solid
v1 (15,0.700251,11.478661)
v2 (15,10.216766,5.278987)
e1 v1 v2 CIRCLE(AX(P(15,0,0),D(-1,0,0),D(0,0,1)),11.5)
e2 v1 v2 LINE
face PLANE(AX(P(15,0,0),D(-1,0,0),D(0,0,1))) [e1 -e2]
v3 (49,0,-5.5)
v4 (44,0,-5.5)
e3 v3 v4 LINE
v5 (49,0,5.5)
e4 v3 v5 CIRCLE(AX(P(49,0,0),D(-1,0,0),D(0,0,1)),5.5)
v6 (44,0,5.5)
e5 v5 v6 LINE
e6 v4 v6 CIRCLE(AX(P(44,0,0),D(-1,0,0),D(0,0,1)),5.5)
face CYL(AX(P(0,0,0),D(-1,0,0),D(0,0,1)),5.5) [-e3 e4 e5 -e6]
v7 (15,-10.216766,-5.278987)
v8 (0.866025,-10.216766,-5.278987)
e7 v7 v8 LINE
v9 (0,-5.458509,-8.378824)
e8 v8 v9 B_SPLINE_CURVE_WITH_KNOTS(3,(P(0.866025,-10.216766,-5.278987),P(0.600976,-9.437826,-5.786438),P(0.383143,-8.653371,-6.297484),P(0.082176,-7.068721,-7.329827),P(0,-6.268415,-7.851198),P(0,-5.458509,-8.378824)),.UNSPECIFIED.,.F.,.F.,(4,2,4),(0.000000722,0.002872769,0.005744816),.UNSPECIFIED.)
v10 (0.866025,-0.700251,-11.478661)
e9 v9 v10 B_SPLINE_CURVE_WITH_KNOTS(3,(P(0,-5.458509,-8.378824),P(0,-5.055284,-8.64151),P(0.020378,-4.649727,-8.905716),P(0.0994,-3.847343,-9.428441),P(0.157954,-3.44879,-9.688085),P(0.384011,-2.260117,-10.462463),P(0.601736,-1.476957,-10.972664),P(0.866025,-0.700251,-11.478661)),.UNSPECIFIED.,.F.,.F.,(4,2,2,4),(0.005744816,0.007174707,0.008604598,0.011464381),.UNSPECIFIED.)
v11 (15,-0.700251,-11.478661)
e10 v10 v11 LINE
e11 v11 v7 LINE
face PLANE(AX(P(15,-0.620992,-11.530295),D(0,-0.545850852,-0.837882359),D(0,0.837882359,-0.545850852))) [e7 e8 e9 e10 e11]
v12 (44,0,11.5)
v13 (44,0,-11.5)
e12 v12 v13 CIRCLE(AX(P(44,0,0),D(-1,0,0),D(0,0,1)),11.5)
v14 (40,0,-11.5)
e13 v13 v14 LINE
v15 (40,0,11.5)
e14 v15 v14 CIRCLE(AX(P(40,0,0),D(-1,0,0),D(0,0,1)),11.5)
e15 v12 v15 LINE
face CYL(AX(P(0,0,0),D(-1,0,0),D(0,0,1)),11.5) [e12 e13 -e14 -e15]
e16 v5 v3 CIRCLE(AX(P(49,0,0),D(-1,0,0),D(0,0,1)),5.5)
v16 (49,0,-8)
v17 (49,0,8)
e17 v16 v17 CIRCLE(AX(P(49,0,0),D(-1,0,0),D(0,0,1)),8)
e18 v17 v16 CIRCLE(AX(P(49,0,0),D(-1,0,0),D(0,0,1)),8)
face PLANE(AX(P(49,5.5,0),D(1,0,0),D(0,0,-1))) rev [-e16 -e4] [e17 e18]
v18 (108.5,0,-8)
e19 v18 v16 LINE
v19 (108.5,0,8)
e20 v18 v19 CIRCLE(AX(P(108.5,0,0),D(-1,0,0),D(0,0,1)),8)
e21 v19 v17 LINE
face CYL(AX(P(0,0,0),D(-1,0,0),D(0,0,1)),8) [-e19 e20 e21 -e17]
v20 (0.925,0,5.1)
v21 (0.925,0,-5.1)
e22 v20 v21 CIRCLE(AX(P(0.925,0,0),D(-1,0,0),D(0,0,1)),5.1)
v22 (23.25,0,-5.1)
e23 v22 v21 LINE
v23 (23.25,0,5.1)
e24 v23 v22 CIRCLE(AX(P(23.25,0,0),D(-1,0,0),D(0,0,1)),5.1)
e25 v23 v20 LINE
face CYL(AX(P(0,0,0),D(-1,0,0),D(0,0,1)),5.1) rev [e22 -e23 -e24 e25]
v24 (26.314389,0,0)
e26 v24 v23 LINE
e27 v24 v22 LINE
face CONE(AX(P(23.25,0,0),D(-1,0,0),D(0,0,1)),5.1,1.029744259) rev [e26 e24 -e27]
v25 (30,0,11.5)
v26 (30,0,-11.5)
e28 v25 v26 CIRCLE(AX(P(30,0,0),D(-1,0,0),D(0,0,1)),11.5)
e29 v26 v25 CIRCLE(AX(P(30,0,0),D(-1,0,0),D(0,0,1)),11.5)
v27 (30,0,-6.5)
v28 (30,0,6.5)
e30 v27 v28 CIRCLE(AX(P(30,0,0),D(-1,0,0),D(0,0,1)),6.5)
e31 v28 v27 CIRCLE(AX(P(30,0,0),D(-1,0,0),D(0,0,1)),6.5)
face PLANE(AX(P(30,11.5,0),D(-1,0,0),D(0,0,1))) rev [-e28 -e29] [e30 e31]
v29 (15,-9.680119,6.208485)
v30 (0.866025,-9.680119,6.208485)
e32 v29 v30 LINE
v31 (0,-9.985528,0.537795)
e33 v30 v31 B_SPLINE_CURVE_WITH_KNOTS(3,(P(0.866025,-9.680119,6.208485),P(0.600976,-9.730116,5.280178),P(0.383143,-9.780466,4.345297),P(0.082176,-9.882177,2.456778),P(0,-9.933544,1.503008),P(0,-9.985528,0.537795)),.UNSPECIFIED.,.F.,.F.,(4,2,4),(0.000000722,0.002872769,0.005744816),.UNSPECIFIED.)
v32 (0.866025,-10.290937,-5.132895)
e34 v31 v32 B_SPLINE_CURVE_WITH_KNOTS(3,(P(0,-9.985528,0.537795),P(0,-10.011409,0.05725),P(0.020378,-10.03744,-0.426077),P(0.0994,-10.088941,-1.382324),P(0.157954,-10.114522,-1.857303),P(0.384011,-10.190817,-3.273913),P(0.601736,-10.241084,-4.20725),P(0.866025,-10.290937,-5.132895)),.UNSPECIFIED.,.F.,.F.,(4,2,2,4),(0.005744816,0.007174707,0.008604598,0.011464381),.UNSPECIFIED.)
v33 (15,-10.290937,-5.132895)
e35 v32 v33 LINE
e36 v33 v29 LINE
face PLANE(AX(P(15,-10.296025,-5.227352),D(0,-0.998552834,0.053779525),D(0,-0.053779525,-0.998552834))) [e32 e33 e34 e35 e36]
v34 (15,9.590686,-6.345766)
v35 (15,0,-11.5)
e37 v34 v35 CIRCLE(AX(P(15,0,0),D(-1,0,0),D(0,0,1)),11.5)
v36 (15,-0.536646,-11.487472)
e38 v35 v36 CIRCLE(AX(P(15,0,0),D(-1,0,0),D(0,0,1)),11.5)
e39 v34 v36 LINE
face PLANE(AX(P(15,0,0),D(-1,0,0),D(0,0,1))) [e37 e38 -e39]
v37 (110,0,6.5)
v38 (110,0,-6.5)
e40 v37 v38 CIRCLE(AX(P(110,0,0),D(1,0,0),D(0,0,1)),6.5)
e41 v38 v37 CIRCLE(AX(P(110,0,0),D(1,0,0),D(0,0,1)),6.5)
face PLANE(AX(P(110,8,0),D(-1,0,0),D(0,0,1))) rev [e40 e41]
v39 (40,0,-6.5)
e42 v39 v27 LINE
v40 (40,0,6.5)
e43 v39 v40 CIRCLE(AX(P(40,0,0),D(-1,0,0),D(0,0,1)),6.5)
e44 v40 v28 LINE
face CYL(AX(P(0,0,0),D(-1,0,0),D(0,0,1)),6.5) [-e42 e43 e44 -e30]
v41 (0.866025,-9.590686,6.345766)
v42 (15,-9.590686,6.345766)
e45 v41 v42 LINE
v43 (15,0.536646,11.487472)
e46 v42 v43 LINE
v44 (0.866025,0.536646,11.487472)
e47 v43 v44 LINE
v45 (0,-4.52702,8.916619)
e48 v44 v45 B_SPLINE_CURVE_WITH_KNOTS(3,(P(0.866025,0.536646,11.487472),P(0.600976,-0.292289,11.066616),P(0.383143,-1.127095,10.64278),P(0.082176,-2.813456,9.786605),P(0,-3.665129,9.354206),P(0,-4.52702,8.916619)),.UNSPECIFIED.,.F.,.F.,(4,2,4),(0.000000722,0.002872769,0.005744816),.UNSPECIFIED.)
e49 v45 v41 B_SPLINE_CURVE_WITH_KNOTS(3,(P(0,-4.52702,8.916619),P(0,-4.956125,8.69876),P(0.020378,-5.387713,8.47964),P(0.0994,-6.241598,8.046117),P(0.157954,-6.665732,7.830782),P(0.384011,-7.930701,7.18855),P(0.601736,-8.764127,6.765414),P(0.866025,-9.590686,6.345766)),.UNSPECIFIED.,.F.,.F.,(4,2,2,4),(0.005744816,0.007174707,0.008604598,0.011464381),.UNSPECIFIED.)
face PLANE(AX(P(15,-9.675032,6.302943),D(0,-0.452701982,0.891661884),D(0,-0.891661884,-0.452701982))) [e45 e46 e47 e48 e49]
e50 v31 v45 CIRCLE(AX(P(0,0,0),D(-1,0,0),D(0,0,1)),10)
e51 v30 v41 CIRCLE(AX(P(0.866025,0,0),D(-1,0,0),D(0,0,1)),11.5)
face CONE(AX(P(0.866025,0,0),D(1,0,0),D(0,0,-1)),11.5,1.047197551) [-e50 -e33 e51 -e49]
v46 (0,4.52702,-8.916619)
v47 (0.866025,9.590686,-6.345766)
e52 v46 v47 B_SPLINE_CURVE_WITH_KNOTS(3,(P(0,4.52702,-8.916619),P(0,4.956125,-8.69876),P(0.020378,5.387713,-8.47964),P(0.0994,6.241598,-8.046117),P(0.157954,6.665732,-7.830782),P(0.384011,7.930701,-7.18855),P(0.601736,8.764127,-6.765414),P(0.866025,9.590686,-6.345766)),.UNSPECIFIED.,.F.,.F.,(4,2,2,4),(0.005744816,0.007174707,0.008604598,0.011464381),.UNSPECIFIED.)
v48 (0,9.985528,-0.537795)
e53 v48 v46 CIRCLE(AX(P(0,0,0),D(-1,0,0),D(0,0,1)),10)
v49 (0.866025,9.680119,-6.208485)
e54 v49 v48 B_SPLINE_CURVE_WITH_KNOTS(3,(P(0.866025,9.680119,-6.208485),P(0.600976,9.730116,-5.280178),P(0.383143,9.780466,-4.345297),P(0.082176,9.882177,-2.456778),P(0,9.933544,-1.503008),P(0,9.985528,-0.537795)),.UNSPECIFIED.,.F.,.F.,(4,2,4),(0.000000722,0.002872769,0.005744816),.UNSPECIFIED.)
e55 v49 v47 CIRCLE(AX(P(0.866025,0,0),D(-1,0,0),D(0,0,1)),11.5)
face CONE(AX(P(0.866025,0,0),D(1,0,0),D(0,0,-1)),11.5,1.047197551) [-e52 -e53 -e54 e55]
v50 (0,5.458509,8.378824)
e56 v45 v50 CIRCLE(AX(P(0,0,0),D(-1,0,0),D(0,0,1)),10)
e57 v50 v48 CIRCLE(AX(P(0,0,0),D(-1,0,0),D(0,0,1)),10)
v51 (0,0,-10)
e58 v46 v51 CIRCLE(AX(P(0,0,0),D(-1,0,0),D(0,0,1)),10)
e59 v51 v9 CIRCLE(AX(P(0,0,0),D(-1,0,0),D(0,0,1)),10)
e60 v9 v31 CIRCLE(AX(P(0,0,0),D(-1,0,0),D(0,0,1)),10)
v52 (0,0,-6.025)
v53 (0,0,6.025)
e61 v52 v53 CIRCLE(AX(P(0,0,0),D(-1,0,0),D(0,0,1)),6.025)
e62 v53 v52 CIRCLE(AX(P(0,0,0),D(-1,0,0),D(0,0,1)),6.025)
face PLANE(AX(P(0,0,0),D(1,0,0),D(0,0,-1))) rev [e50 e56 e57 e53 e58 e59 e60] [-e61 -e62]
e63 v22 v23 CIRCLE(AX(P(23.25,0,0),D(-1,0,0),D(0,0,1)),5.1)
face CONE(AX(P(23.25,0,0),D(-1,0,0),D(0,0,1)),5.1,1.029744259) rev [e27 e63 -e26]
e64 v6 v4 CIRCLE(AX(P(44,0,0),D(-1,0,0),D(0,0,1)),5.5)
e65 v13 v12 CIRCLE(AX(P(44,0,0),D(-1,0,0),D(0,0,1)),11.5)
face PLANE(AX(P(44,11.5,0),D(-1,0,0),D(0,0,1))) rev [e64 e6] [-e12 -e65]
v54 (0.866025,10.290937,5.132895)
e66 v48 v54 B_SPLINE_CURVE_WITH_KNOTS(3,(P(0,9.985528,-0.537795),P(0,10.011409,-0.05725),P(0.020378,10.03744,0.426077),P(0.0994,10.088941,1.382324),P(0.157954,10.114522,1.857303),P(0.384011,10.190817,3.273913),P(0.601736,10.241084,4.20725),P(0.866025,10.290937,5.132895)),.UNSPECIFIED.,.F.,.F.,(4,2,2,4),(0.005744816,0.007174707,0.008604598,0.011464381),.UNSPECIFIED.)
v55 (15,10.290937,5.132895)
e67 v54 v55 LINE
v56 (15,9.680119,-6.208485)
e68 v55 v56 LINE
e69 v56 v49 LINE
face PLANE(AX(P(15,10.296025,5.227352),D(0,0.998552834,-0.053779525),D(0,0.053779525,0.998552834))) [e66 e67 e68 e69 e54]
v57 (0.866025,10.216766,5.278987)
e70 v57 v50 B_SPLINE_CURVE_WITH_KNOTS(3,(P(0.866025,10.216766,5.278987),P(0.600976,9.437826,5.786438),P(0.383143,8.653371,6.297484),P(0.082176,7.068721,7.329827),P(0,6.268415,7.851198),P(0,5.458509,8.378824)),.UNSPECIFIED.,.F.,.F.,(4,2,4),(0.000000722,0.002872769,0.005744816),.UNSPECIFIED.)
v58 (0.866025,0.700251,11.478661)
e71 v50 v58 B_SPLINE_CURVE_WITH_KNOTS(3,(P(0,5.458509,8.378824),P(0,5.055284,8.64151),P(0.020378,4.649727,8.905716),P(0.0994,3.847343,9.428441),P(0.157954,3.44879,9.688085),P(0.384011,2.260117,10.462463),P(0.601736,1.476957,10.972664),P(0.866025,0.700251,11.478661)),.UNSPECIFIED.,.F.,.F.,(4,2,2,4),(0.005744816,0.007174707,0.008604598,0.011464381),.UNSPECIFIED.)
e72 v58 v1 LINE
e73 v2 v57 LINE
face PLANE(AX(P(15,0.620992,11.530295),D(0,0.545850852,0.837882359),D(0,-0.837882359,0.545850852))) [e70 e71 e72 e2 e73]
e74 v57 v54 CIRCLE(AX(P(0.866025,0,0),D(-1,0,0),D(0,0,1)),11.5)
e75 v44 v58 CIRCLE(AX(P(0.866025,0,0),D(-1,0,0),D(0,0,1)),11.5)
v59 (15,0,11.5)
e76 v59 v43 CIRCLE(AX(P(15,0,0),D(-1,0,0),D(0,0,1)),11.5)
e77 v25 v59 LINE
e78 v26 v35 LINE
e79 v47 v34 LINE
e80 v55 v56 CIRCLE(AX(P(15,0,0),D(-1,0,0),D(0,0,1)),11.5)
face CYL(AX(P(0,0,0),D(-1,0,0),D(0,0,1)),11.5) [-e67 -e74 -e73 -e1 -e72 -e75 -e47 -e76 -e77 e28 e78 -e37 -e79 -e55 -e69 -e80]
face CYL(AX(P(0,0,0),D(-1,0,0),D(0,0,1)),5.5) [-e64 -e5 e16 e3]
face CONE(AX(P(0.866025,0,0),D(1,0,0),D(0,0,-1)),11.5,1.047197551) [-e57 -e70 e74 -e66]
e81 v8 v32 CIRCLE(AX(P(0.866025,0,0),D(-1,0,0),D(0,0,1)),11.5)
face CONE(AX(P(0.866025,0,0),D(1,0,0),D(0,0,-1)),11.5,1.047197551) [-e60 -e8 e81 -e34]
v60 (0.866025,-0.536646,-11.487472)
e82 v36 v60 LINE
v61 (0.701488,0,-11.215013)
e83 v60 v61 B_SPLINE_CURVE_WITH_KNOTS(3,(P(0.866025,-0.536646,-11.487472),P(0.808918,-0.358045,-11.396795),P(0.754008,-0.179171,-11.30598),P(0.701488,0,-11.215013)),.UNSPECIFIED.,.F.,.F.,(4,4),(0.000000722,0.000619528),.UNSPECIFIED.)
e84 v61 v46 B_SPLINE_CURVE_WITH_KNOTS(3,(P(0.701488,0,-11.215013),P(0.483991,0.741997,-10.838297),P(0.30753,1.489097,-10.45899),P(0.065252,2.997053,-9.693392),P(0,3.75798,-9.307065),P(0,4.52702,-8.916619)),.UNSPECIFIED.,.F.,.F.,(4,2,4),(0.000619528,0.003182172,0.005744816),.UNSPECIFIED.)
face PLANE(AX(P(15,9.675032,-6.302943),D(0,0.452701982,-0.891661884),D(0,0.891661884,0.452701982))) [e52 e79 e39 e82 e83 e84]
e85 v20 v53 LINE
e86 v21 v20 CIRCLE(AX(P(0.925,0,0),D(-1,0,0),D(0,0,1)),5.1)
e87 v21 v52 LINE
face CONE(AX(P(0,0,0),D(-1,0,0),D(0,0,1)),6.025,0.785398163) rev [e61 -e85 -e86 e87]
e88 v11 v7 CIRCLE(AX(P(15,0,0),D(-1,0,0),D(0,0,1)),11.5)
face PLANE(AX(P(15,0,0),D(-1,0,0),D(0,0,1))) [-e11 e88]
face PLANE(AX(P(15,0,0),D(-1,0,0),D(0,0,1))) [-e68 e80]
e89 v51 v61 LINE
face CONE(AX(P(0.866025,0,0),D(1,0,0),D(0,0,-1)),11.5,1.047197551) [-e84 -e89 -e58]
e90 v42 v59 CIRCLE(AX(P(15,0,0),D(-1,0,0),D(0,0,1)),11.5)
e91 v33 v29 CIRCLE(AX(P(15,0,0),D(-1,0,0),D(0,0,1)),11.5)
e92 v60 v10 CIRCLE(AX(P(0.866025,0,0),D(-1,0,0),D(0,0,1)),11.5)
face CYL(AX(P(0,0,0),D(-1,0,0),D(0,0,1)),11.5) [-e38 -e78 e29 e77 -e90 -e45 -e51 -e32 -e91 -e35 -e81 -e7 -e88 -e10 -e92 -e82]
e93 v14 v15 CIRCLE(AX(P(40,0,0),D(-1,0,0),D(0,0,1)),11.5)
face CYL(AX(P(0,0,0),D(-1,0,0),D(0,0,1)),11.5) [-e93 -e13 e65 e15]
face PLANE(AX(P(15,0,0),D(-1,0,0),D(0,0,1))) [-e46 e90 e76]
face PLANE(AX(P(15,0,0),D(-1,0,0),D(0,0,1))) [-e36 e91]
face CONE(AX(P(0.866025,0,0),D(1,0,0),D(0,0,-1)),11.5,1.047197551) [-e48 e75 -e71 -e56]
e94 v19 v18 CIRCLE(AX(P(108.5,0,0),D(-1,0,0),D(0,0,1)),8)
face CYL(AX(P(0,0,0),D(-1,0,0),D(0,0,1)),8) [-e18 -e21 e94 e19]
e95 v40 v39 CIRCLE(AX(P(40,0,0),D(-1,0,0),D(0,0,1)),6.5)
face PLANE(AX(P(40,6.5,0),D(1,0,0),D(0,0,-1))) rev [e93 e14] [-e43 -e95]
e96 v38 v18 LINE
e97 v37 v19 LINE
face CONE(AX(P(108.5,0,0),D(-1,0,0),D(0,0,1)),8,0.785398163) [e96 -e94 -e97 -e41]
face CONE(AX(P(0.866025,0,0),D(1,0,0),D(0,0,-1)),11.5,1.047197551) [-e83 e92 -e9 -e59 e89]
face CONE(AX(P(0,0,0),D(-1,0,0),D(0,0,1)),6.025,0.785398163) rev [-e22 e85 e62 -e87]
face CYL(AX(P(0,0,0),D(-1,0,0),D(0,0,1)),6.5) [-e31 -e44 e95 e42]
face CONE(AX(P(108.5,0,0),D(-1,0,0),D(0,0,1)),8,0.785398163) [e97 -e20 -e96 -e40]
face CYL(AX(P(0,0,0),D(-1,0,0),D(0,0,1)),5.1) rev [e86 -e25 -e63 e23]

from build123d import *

# Parameters (mm, degrees)
M12_TAPPED_HOLE1_D           = 10.2
M12_TAPPED_HOLE1_DEPTH       = 23.25
M12_TAPPED_HOLE1_CSINK_D     = 12.05
M12_TAPPED_HOLE1_CSINK_ANGLE = 90
M12_TAPPED_HOLE1_TIP         = 3.064389157
SKETCH4_R                    = 21.574990141
CUT_EXTRUDE1_DEPTH           = 15
CHAMFER1_SIZE                = 1.5


with BuildPart() as part:
    # Sketch1 → Revolve1 (revolve)
    with BuildSketch(Plane.XY, mode=Mode.PRIVATE) as revolve1_sk:
        Polygon((0, 0), (0, 10), (0.866025404, 11.5), (30, 11.5), (30, 6.5), (40, 6.5), (40, 11.5), (44, 11.5), (44, 5.5), (49, 5.5), (49, 8), (110, 8), (110, 0), align=None)
    revolve(revolve1_sk.sketch.rotate(Axis((0, 0, 0), (1, 0, 0)), 90), axis=Axis((0, 0, 0), (1, 0, 0)))

    # M12 Tapped Hole1
    with Locations(Plane(origin=(0, 0, 0), x_dir=(0, 0, -1), z_dir=(-1, 0, 0))):
        with Locations((0, 0)):
            CounterSinkHole(M12_TAPPED_HOLE1_D / 2, M12_TAPPED_HOLE1_CSINK_D / 2, depth=M12_TAPPED_HOLE1_DEPTH, counter_sink_angle=M12_TAPPED_HOLE1_CSINK_ANGLE)
            with Locations((0, 0, -(M12_TAPPED_HOLE1_DEPTH + M12_TAPPED_HOLE1_TIP / 2))):  # 118° drill point
                Cone(0, M12_TAPPED_HOLE1_D / 2, M12_TAPPED_HOLE1_TIP, mode=Mode.SUBTRACT)

    # Sketch4 → Cut-Extrude1 (cut)
    with BuildSketch(Plane.ZY):
        Circle(SKETCH4_R)
        Polygon((5.227352222, 10.296024576), (-6.30294273, 9.675032107), (-11.530294952, -0.620992469), (-5.227352222, -10.296024576), (6.30294273, -9.675032107), (11.530294952, 0.620992469), align=None, mode=Mode.SUBTRACT)
    extrude(amount=-CUT_EXTRUDE1_DEPTH, mode=Mode.SUBTRACT)

    # Chamfer1
    chamfer1_edges = [part.edges().sort_by_distance(p)[0] for p in [
        (110, 0, -8),
    ]]
    chamfer(chamfer1_edges, length=CHAMFER1_SIZE)


solid = part.part
